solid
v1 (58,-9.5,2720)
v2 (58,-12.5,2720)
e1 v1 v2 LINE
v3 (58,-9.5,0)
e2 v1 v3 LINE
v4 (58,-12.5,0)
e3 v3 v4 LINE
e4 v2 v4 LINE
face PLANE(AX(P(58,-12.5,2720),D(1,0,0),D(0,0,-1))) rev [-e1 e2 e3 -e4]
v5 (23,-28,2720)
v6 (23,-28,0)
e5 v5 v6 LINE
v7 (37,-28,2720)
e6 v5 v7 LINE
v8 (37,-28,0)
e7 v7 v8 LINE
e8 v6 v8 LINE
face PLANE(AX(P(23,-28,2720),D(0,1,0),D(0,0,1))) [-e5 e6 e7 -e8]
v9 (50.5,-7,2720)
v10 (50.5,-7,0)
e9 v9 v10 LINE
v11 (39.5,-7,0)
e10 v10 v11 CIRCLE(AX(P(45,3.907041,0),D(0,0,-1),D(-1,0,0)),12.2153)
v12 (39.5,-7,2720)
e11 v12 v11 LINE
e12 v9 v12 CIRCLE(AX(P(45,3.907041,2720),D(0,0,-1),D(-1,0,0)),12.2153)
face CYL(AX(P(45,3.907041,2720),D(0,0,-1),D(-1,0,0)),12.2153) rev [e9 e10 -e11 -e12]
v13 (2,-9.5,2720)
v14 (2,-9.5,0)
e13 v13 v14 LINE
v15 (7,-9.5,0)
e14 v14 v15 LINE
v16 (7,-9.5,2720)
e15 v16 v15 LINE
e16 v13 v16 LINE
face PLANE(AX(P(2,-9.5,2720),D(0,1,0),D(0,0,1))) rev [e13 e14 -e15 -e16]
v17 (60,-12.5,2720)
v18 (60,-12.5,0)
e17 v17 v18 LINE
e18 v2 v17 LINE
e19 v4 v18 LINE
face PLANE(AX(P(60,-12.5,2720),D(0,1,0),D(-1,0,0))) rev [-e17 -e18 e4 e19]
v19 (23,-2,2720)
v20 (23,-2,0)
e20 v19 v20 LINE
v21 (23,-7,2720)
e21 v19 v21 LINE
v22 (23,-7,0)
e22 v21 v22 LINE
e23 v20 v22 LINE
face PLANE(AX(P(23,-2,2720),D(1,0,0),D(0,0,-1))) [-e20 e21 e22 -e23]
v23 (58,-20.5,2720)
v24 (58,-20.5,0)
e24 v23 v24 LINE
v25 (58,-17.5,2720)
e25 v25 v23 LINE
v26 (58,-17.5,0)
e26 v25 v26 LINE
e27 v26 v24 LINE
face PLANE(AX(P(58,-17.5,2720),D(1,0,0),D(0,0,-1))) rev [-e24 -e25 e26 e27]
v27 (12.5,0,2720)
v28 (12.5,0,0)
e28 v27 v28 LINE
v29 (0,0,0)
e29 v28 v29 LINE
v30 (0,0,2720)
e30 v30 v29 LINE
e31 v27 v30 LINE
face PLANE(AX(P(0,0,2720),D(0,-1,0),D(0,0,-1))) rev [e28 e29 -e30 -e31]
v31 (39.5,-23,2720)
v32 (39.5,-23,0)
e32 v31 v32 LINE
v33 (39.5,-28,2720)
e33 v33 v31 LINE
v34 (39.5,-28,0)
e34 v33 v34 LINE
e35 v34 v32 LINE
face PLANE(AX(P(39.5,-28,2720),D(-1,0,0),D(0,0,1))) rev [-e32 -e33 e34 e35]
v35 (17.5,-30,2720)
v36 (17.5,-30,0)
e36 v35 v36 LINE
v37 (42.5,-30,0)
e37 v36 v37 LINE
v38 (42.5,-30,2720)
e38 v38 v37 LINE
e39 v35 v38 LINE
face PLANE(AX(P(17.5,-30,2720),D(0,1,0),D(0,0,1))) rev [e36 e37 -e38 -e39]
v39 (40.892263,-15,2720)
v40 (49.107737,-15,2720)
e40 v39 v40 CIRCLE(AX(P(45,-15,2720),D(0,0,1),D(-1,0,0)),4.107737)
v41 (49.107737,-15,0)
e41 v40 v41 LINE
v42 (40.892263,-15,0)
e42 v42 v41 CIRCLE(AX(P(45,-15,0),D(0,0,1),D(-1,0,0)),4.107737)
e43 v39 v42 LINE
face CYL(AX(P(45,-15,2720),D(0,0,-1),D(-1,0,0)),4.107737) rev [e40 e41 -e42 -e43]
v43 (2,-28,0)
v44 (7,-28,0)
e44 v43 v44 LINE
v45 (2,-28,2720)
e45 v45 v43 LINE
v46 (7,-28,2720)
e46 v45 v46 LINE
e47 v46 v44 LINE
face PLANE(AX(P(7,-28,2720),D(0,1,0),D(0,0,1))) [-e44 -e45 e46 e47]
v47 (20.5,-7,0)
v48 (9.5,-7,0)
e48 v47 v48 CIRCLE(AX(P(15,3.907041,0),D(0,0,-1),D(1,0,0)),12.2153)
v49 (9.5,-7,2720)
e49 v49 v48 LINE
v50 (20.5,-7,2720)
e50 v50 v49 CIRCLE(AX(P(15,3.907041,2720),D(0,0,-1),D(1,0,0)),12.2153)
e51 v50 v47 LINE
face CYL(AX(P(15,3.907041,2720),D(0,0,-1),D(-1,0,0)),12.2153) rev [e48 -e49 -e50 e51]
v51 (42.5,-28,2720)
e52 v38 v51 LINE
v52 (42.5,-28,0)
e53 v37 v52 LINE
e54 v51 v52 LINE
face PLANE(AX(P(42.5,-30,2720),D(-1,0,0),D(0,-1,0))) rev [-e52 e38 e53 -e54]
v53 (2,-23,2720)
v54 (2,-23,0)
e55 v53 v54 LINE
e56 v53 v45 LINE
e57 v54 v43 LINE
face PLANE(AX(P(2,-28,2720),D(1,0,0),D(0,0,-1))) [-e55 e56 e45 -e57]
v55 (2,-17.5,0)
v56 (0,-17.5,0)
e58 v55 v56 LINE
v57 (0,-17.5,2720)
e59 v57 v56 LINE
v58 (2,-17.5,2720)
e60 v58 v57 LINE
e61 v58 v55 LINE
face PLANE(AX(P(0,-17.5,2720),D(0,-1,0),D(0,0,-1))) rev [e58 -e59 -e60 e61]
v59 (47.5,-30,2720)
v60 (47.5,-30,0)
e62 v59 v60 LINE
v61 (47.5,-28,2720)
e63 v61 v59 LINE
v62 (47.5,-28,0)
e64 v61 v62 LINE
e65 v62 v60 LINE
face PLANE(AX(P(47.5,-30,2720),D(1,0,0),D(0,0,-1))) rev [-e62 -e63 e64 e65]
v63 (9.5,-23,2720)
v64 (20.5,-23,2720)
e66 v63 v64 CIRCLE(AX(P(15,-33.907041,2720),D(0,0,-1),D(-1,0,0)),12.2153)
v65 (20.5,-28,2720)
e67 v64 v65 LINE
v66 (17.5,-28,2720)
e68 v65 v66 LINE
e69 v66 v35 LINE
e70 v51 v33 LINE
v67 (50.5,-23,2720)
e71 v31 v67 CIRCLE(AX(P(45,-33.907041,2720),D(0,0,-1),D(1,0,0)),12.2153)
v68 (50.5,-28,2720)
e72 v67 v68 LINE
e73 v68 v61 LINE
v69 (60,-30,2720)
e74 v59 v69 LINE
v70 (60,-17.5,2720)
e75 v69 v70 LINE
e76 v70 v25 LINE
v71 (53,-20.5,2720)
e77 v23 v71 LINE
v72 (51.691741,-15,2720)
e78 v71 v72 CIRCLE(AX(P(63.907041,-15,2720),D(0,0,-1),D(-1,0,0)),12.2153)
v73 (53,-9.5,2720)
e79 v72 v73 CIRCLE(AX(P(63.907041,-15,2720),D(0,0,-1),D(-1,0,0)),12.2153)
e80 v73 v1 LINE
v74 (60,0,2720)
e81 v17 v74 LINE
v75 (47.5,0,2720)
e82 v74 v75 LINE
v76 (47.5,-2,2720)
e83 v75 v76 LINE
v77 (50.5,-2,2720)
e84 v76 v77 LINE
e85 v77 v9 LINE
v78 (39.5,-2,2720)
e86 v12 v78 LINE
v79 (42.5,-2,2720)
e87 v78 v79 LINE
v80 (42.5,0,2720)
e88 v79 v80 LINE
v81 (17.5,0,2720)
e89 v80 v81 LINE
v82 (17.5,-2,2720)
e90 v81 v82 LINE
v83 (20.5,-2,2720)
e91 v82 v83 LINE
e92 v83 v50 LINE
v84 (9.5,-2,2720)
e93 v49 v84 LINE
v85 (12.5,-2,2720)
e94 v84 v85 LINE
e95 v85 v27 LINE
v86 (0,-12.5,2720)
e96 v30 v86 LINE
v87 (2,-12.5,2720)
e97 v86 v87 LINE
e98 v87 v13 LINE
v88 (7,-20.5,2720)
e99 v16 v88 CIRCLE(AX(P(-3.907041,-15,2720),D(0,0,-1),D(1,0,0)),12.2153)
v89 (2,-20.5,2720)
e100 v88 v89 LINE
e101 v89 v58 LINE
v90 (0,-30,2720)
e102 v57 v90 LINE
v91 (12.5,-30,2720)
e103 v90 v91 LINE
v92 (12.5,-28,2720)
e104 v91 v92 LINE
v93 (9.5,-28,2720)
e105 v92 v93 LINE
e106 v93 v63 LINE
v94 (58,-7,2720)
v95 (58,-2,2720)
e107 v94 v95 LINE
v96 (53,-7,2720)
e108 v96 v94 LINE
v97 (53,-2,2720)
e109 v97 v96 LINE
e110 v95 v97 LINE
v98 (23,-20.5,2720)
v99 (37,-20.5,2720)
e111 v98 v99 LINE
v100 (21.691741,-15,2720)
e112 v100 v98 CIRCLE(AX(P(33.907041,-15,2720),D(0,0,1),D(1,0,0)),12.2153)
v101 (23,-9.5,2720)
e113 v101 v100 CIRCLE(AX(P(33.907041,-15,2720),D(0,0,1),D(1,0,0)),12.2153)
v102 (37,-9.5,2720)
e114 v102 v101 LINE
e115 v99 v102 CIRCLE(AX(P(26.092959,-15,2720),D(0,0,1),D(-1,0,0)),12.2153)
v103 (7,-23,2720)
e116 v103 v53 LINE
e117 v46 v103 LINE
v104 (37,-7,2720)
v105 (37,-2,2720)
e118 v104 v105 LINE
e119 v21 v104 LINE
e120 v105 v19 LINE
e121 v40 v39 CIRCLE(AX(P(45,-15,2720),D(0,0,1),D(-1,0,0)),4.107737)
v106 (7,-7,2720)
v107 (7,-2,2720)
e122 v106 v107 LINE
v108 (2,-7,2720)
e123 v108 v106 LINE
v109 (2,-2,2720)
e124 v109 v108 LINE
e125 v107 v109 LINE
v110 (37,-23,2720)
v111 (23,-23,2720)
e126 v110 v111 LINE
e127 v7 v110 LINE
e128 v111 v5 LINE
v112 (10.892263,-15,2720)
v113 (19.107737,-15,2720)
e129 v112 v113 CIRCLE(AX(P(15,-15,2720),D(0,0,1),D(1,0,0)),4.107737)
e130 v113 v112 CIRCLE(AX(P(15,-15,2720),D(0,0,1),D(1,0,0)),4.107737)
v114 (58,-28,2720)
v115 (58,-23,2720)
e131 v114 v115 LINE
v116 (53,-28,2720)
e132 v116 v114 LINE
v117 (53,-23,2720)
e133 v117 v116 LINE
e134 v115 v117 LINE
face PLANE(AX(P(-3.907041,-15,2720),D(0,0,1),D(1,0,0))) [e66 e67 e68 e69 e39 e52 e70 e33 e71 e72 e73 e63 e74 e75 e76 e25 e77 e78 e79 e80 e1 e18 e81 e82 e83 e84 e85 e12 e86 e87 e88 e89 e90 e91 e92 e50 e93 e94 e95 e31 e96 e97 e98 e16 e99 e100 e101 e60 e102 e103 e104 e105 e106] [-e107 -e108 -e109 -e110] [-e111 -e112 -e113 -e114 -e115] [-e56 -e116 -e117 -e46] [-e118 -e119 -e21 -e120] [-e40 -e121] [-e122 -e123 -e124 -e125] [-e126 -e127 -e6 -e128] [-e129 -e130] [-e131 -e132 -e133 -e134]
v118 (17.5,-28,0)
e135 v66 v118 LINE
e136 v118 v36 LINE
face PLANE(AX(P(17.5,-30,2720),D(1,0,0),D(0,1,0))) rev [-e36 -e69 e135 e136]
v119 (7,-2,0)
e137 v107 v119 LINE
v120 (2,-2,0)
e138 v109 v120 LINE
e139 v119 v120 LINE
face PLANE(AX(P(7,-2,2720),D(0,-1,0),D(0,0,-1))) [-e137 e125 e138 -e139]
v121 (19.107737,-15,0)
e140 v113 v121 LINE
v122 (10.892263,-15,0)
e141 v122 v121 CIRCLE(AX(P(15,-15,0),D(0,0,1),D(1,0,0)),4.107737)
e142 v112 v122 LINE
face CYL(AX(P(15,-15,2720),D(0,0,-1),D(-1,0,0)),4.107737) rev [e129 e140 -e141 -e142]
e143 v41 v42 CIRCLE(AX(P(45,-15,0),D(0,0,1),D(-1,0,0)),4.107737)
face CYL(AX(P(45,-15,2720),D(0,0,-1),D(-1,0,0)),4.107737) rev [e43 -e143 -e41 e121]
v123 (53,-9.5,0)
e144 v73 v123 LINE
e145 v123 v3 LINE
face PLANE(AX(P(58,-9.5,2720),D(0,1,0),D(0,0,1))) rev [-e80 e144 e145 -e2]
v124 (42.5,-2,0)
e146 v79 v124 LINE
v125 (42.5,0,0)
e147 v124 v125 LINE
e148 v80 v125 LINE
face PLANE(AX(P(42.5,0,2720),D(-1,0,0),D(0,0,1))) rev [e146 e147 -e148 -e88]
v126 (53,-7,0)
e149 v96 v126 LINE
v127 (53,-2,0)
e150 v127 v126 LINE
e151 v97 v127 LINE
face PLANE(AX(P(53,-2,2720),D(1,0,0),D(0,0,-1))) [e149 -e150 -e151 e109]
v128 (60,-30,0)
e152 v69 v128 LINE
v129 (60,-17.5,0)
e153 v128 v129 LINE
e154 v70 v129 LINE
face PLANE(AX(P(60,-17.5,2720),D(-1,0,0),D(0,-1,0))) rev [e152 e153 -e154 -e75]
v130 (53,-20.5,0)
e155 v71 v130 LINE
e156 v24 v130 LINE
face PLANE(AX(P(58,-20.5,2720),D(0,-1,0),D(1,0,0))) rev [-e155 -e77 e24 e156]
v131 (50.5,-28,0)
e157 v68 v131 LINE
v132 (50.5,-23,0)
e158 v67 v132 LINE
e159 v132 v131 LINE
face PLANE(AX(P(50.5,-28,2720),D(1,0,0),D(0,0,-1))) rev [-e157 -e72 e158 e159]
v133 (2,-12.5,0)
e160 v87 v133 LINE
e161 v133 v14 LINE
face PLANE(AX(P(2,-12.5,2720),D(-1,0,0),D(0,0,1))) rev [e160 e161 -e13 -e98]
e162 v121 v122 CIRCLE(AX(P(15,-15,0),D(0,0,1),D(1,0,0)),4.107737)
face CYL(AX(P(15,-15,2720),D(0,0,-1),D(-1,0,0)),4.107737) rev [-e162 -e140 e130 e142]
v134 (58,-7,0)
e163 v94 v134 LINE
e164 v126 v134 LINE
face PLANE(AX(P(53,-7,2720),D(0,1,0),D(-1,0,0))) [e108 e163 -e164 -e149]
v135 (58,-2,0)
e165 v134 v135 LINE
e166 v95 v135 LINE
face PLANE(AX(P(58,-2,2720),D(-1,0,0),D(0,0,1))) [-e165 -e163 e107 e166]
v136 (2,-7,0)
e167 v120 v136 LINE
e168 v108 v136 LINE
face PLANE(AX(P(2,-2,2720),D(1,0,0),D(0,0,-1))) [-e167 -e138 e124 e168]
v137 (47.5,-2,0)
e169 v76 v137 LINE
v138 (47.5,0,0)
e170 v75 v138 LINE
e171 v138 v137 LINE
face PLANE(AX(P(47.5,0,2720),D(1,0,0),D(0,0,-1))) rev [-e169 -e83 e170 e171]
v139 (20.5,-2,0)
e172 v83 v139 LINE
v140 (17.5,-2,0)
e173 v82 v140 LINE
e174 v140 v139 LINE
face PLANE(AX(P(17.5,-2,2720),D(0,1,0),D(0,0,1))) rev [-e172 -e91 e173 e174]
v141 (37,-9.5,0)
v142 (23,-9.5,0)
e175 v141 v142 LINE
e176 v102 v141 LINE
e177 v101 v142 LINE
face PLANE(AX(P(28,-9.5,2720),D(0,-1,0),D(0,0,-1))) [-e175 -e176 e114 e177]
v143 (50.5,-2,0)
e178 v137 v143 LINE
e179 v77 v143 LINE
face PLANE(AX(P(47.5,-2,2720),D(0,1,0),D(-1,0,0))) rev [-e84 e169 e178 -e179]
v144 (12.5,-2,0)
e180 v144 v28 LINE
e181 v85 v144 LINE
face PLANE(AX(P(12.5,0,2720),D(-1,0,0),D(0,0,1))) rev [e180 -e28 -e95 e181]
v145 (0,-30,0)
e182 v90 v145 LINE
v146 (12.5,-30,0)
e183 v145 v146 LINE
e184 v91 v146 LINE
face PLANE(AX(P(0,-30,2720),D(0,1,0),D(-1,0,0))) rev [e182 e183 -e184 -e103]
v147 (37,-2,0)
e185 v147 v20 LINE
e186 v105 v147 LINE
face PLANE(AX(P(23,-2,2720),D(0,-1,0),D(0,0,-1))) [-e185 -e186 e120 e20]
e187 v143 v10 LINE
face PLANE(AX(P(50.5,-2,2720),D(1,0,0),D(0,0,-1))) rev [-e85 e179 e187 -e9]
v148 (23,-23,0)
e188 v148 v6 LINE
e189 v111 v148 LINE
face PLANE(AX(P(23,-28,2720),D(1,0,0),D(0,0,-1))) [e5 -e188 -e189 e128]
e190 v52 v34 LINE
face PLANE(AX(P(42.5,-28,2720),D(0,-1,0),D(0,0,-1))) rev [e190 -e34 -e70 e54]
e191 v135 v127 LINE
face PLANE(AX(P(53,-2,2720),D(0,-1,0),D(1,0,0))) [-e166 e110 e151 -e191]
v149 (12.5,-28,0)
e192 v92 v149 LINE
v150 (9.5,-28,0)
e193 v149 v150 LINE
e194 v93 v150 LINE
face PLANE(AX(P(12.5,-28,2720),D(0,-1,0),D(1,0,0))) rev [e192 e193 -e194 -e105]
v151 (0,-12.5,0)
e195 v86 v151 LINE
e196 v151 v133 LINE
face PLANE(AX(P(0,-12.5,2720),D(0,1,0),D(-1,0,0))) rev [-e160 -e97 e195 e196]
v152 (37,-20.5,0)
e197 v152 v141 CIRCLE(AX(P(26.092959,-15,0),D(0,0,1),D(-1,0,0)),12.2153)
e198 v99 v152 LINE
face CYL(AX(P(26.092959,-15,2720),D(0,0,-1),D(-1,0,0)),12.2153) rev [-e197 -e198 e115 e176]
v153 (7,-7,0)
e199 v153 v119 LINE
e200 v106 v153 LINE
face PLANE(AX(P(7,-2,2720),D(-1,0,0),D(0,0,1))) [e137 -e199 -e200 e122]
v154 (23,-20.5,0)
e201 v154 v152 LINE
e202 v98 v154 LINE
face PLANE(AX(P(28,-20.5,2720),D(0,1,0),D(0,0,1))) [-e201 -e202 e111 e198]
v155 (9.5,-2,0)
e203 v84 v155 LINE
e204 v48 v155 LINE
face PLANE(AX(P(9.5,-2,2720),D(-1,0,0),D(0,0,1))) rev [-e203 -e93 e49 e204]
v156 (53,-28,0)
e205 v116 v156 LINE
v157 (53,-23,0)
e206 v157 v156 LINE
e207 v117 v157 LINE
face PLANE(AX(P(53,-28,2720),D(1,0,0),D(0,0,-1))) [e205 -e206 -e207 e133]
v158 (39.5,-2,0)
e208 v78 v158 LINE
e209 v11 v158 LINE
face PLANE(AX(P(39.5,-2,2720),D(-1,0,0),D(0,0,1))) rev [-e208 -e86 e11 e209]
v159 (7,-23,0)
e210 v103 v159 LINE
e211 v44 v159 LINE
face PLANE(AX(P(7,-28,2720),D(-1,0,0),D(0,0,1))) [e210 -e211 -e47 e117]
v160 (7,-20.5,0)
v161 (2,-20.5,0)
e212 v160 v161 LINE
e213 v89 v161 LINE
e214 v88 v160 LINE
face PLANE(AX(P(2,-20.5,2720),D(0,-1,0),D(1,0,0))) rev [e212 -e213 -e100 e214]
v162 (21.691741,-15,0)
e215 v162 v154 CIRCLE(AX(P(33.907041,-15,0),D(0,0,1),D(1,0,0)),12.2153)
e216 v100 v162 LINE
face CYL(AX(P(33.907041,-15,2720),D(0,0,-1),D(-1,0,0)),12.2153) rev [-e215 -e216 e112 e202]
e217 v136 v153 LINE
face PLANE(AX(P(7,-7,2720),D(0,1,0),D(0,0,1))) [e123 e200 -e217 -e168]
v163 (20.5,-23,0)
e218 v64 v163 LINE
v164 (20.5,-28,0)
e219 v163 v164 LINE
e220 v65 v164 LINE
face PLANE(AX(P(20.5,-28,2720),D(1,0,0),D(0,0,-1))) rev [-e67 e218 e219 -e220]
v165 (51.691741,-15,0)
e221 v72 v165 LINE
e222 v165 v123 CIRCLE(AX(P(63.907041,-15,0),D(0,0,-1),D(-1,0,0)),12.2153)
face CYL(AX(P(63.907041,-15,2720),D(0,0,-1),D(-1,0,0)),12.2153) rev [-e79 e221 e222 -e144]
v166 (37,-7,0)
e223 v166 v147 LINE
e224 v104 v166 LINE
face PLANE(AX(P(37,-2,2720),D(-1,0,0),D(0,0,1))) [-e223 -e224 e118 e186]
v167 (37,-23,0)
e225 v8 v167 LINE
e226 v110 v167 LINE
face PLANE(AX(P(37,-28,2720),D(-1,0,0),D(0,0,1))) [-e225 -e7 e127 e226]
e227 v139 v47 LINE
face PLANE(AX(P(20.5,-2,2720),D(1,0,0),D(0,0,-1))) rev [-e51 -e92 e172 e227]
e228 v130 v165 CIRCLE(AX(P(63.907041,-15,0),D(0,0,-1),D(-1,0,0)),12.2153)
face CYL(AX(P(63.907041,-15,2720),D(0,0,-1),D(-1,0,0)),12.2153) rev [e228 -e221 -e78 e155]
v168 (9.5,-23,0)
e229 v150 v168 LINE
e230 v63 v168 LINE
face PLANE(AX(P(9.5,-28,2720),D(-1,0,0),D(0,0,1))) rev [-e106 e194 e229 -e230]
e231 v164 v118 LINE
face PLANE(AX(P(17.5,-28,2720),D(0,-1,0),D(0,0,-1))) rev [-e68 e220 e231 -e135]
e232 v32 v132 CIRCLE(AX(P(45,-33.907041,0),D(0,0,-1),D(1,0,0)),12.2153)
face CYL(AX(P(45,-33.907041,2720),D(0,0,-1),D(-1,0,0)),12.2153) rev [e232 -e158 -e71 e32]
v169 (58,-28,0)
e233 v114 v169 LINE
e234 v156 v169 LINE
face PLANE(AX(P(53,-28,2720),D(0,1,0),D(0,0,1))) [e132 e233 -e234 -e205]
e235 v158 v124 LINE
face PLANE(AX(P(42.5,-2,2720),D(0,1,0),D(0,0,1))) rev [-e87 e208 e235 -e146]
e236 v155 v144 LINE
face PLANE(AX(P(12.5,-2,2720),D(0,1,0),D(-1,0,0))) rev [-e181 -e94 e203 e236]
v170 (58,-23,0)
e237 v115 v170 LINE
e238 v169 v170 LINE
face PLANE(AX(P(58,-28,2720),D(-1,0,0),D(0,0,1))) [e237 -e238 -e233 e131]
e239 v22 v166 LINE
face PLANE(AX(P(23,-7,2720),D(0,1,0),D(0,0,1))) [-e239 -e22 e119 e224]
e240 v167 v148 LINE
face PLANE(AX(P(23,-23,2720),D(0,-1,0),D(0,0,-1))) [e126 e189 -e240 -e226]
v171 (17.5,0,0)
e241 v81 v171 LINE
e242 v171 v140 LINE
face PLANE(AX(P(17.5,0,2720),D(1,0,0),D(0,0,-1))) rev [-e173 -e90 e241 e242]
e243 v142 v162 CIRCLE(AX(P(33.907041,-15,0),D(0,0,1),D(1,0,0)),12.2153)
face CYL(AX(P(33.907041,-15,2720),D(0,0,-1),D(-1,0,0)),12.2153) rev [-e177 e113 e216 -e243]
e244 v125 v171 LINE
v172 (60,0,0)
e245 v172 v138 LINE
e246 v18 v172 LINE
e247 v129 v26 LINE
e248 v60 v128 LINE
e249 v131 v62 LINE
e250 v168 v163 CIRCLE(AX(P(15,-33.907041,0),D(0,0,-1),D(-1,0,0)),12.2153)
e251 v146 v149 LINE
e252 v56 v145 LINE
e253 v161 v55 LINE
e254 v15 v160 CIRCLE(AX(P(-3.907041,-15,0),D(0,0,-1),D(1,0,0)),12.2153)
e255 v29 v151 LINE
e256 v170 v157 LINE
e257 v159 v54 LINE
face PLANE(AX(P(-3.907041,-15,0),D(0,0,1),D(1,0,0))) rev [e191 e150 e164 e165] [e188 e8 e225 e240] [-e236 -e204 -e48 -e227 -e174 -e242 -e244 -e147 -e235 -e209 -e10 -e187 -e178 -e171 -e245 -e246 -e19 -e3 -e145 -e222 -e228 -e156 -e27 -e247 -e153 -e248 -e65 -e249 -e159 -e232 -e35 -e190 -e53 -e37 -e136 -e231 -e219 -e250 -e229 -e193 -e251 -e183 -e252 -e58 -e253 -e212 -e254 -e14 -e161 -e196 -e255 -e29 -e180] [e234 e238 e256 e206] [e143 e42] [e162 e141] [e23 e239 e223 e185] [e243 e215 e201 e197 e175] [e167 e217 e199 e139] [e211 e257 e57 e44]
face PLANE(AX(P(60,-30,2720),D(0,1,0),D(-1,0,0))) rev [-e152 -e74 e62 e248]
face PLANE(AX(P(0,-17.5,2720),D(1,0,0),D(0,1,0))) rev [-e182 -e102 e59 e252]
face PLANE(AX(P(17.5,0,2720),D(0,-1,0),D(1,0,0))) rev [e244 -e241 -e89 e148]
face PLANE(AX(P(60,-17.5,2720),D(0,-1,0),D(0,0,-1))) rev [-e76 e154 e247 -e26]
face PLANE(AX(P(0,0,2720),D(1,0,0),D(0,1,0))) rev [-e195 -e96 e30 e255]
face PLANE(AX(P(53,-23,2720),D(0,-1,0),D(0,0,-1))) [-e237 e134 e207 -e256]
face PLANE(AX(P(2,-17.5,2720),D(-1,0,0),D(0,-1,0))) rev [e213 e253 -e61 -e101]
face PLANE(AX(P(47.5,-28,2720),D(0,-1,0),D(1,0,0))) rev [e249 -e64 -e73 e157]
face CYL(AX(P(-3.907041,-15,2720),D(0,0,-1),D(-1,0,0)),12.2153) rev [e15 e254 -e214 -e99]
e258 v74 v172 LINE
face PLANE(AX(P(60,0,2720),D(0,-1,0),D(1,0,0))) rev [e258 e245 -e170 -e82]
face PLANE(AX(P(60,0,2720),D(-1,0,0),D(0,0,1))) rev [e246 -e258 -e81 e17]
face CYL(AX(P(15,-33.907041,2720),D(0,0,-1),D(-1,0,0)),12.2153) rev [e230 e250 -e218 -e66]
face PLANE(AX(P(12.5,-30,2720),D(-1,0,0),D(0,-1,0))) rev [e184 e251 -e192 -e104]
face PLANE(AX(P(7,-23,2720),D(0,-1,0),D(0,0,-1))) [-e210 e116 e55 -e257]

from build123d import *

# Parameters (mm, degrees)
SKETCH_1_R          = 4.1077368
SKETCH_1_W          = 5
SKETCH_1_H          = 5
EXTRUDE_1_DEPTH     = 2720
SKETCH_2_W          = 4
SKETCH_2_H          = 5
CUT_EXTRUDE_1_DEPTH = 2721.827080136
SKETCH_3_W          = 4
SKETCH_3_H          = 11
CUT_EXTRUDE_2_DEPTH = 2721.827080136


with BuildPart() as part:
    # 草图1 → 拉伸1 (new body)
    with BuildSketch(Plane.XY):
        with BuildLine():
            Line((12.5, 0), (12.5, -2))
            Line((12.5, -2), (9.5, -2))
            Line((9.5, -2), (9.5, -7))
            ThreePointArc((9.5, -7), (15, -8.308258509), (20.5, -7))
            Line((20.5, -7), (20.5, -2))
            Line((20.5, -2), (17.5, -2))
            Line((17.5, -2), (17.5, 0))
            Line((17.5, 0), (42.5, 0))
            Line((42.5, 0), (42.5, -2))
            Line((42.5, -2), (39.5, -2))
            Line((39.5, -2), (39.5, -7))
            ThreePointArc((39.5, -7), (45, -8.308258509), (50.5, -7))
            Line((50.5, -7), (50.5, -2))
            Line((50.5, -2), (47.5, -2))
            Line((47.5, -2), (47.5, 0))
            Line((47.5, 0), (60, 0))
            Line((60, 0), (60, -12.5))
            Line((60, -12.5), (58, -12.5))
            Line((58, -12.5), (58, -9.5))
            Line((58, -9.5), (53, -9.5))
            ThreePointArc((53, -9.5), (51.691741491, -15), (53, -20.5))
            Line((53, -20.5), (58, -20.5))
            Line((58, -20.5), (58, -17.5))
            Line((58, -17.5), (60, -17.5))
            Line((60, -17.5), (60, -30))
            Line((60, -30), (47.5, -30))
            Line((47.5, -30), (47.5, -28))
            Line((47.5, -28), (50.5, -28))
            Line((50.5, -28), (50.5, -23))
            ThreePointArc((50.5, -23), (45, -21.691741491), (39.5, -23))
            Line((39.5, -23), (39.5, -28))
            Line((39.5, -28), (42.5, -28))
            Line((42.5, -28), (42.5, -30))
            Line((42.5, -30), (17.5, -30))
            Line((17.5, -30), (17.5, -28))
            Line((17.5, -28), (20.5, -28))
            Line((20.5, -28), (20.5, -23))
            ThreePointArc((20.5, -23), (15, -21.691741491), (9.5, -23))
            Line((9.5, -23), (9.5, -28))
            Line((9.5, -28), (12.5, -28))
            Line((12.5, -28), (12.5, -30))
            Line((12.5, -30), (0, -30))
            Line((0, -30), (0, -17.5))
            Line((0, -17.5), (2, -17.5))
            Line((2, -17.5), (2, -20.5))
            Line((2, -20.5), (7, -20.5))
            ThreePointArc((7, -20.5), (8.308258509, -15), (7, -9.5))
            Line((7, -9.5), (2, -9.5))
            Line((2, -9.5), (2, -12.5))
            Line((2, -12.5), (0, -12.5))
            Line((0, -12.5), (0, 0))
            Line((0, 0), (12.5, 0))
        make_face()
        with Locations((15, -15)):
            Circle(SKETCH_1_R, mode=Mode.SUBTRACT)
        with Locations(Location((45, -15, 0), (0, 0, 180))):
            Circle(SKETCH_1_R, mode=Mode.SUBTRACT)
        with BuildLine():
            Line((32, -12.5), (28, -12.5))
            Line((28, -12.5), (28, -9.5))
            Line((28, -9.5), (23, -9.5))
            ThreePointArc((23, -9.5), (21.691741491, -15), (23, -20.5))
            Line((23, -20.5), (28, -20.5))
            Line((28, -20.5), (28, -17.5))
            Line((28, -17.5), (32, -17.5))
            Line((32, -17.5), (32, -20.5))
            Line((32, -20.5), (37, -20.5))
            ThreePointArc((37, -20.5), (38.308258509, -15), (37, -9.5))
            Line((37, -9.5), (32, -9.5))
            Line((32, -9.5), (32, -12.5))
        make_face(mode=Mode.SUBTRACT)
        with Locations((55.5, -4.5)):
            Rectangle(SKETCH_1_W, SKETCH_1_H, mode=Mode.SUBTRACT)
        with Locations((25.5, -25.5)):
            Rectangle(SKETCH_1_W, SKETCH_1_H, mode=Mode.SUBTRACT)
        with Locations((25.5, -4.5)):
            Rectangle(SKETCH_1_W, SKETCH_1_H, mode=Mode.SUBTRACT)
        with Locations((4.5, -25.5)):
            Rectangle(SKETCH_1_W, SKETCH_1_H, mode=Mode.SUBTRACT)
        with Locations((4.5, -4.5)):
            Rectangle(SKETCH_1_W, SKETCH_1_H, mode=Mode.SUBTRACT)
        with Locations((55.5, -25.5)):
            Rectangle(SKETCH_1_W, SKETCH_1_H, mode=Mode.SUBTRACT)
        with Locations((34.5, -25.5)):
            Rectangle(SKETCH_1_W, SKETCH_1_H, mode=Mode.SUBTRACT)
        with Locations((34.5, -4.5)):
            Rectangle(SKETCH_1_W, SKETCH_1_H, mode=Mode.SUBTRACT)
    extrude(amount=EXTRUDE_1_DEPTH)

    # 草图2 → 切除-拉伸1 (cut, through all)
    with BuildSketch(Plane.XY.offset(2720)):
        with Locations((30, -4.5)):
            Rectangle(SKETCH_2_W, SKETCH_2_H)
        with Locations((30, -25.5)):
            Rectangle(SKETCH_2_W, SKETCH_2_H)
    extrude(amount=-CUT_EXTRUDE_1_DEPTH, mode=Mode.SUBTRACT)

    # 草图3 → 切除-拉伸2 (cut, through all)
    with BuildSketch(Plane.XY.offset(2720)):
        with Locations((30, -15)):
            Rectangle(SKETCH_3_W, SKETCH_3_H)
    extrude(amount=-CUT_EXTRUDE_2_DEPTH, mode=Mode.SUBTRACT)


solid = part.part
